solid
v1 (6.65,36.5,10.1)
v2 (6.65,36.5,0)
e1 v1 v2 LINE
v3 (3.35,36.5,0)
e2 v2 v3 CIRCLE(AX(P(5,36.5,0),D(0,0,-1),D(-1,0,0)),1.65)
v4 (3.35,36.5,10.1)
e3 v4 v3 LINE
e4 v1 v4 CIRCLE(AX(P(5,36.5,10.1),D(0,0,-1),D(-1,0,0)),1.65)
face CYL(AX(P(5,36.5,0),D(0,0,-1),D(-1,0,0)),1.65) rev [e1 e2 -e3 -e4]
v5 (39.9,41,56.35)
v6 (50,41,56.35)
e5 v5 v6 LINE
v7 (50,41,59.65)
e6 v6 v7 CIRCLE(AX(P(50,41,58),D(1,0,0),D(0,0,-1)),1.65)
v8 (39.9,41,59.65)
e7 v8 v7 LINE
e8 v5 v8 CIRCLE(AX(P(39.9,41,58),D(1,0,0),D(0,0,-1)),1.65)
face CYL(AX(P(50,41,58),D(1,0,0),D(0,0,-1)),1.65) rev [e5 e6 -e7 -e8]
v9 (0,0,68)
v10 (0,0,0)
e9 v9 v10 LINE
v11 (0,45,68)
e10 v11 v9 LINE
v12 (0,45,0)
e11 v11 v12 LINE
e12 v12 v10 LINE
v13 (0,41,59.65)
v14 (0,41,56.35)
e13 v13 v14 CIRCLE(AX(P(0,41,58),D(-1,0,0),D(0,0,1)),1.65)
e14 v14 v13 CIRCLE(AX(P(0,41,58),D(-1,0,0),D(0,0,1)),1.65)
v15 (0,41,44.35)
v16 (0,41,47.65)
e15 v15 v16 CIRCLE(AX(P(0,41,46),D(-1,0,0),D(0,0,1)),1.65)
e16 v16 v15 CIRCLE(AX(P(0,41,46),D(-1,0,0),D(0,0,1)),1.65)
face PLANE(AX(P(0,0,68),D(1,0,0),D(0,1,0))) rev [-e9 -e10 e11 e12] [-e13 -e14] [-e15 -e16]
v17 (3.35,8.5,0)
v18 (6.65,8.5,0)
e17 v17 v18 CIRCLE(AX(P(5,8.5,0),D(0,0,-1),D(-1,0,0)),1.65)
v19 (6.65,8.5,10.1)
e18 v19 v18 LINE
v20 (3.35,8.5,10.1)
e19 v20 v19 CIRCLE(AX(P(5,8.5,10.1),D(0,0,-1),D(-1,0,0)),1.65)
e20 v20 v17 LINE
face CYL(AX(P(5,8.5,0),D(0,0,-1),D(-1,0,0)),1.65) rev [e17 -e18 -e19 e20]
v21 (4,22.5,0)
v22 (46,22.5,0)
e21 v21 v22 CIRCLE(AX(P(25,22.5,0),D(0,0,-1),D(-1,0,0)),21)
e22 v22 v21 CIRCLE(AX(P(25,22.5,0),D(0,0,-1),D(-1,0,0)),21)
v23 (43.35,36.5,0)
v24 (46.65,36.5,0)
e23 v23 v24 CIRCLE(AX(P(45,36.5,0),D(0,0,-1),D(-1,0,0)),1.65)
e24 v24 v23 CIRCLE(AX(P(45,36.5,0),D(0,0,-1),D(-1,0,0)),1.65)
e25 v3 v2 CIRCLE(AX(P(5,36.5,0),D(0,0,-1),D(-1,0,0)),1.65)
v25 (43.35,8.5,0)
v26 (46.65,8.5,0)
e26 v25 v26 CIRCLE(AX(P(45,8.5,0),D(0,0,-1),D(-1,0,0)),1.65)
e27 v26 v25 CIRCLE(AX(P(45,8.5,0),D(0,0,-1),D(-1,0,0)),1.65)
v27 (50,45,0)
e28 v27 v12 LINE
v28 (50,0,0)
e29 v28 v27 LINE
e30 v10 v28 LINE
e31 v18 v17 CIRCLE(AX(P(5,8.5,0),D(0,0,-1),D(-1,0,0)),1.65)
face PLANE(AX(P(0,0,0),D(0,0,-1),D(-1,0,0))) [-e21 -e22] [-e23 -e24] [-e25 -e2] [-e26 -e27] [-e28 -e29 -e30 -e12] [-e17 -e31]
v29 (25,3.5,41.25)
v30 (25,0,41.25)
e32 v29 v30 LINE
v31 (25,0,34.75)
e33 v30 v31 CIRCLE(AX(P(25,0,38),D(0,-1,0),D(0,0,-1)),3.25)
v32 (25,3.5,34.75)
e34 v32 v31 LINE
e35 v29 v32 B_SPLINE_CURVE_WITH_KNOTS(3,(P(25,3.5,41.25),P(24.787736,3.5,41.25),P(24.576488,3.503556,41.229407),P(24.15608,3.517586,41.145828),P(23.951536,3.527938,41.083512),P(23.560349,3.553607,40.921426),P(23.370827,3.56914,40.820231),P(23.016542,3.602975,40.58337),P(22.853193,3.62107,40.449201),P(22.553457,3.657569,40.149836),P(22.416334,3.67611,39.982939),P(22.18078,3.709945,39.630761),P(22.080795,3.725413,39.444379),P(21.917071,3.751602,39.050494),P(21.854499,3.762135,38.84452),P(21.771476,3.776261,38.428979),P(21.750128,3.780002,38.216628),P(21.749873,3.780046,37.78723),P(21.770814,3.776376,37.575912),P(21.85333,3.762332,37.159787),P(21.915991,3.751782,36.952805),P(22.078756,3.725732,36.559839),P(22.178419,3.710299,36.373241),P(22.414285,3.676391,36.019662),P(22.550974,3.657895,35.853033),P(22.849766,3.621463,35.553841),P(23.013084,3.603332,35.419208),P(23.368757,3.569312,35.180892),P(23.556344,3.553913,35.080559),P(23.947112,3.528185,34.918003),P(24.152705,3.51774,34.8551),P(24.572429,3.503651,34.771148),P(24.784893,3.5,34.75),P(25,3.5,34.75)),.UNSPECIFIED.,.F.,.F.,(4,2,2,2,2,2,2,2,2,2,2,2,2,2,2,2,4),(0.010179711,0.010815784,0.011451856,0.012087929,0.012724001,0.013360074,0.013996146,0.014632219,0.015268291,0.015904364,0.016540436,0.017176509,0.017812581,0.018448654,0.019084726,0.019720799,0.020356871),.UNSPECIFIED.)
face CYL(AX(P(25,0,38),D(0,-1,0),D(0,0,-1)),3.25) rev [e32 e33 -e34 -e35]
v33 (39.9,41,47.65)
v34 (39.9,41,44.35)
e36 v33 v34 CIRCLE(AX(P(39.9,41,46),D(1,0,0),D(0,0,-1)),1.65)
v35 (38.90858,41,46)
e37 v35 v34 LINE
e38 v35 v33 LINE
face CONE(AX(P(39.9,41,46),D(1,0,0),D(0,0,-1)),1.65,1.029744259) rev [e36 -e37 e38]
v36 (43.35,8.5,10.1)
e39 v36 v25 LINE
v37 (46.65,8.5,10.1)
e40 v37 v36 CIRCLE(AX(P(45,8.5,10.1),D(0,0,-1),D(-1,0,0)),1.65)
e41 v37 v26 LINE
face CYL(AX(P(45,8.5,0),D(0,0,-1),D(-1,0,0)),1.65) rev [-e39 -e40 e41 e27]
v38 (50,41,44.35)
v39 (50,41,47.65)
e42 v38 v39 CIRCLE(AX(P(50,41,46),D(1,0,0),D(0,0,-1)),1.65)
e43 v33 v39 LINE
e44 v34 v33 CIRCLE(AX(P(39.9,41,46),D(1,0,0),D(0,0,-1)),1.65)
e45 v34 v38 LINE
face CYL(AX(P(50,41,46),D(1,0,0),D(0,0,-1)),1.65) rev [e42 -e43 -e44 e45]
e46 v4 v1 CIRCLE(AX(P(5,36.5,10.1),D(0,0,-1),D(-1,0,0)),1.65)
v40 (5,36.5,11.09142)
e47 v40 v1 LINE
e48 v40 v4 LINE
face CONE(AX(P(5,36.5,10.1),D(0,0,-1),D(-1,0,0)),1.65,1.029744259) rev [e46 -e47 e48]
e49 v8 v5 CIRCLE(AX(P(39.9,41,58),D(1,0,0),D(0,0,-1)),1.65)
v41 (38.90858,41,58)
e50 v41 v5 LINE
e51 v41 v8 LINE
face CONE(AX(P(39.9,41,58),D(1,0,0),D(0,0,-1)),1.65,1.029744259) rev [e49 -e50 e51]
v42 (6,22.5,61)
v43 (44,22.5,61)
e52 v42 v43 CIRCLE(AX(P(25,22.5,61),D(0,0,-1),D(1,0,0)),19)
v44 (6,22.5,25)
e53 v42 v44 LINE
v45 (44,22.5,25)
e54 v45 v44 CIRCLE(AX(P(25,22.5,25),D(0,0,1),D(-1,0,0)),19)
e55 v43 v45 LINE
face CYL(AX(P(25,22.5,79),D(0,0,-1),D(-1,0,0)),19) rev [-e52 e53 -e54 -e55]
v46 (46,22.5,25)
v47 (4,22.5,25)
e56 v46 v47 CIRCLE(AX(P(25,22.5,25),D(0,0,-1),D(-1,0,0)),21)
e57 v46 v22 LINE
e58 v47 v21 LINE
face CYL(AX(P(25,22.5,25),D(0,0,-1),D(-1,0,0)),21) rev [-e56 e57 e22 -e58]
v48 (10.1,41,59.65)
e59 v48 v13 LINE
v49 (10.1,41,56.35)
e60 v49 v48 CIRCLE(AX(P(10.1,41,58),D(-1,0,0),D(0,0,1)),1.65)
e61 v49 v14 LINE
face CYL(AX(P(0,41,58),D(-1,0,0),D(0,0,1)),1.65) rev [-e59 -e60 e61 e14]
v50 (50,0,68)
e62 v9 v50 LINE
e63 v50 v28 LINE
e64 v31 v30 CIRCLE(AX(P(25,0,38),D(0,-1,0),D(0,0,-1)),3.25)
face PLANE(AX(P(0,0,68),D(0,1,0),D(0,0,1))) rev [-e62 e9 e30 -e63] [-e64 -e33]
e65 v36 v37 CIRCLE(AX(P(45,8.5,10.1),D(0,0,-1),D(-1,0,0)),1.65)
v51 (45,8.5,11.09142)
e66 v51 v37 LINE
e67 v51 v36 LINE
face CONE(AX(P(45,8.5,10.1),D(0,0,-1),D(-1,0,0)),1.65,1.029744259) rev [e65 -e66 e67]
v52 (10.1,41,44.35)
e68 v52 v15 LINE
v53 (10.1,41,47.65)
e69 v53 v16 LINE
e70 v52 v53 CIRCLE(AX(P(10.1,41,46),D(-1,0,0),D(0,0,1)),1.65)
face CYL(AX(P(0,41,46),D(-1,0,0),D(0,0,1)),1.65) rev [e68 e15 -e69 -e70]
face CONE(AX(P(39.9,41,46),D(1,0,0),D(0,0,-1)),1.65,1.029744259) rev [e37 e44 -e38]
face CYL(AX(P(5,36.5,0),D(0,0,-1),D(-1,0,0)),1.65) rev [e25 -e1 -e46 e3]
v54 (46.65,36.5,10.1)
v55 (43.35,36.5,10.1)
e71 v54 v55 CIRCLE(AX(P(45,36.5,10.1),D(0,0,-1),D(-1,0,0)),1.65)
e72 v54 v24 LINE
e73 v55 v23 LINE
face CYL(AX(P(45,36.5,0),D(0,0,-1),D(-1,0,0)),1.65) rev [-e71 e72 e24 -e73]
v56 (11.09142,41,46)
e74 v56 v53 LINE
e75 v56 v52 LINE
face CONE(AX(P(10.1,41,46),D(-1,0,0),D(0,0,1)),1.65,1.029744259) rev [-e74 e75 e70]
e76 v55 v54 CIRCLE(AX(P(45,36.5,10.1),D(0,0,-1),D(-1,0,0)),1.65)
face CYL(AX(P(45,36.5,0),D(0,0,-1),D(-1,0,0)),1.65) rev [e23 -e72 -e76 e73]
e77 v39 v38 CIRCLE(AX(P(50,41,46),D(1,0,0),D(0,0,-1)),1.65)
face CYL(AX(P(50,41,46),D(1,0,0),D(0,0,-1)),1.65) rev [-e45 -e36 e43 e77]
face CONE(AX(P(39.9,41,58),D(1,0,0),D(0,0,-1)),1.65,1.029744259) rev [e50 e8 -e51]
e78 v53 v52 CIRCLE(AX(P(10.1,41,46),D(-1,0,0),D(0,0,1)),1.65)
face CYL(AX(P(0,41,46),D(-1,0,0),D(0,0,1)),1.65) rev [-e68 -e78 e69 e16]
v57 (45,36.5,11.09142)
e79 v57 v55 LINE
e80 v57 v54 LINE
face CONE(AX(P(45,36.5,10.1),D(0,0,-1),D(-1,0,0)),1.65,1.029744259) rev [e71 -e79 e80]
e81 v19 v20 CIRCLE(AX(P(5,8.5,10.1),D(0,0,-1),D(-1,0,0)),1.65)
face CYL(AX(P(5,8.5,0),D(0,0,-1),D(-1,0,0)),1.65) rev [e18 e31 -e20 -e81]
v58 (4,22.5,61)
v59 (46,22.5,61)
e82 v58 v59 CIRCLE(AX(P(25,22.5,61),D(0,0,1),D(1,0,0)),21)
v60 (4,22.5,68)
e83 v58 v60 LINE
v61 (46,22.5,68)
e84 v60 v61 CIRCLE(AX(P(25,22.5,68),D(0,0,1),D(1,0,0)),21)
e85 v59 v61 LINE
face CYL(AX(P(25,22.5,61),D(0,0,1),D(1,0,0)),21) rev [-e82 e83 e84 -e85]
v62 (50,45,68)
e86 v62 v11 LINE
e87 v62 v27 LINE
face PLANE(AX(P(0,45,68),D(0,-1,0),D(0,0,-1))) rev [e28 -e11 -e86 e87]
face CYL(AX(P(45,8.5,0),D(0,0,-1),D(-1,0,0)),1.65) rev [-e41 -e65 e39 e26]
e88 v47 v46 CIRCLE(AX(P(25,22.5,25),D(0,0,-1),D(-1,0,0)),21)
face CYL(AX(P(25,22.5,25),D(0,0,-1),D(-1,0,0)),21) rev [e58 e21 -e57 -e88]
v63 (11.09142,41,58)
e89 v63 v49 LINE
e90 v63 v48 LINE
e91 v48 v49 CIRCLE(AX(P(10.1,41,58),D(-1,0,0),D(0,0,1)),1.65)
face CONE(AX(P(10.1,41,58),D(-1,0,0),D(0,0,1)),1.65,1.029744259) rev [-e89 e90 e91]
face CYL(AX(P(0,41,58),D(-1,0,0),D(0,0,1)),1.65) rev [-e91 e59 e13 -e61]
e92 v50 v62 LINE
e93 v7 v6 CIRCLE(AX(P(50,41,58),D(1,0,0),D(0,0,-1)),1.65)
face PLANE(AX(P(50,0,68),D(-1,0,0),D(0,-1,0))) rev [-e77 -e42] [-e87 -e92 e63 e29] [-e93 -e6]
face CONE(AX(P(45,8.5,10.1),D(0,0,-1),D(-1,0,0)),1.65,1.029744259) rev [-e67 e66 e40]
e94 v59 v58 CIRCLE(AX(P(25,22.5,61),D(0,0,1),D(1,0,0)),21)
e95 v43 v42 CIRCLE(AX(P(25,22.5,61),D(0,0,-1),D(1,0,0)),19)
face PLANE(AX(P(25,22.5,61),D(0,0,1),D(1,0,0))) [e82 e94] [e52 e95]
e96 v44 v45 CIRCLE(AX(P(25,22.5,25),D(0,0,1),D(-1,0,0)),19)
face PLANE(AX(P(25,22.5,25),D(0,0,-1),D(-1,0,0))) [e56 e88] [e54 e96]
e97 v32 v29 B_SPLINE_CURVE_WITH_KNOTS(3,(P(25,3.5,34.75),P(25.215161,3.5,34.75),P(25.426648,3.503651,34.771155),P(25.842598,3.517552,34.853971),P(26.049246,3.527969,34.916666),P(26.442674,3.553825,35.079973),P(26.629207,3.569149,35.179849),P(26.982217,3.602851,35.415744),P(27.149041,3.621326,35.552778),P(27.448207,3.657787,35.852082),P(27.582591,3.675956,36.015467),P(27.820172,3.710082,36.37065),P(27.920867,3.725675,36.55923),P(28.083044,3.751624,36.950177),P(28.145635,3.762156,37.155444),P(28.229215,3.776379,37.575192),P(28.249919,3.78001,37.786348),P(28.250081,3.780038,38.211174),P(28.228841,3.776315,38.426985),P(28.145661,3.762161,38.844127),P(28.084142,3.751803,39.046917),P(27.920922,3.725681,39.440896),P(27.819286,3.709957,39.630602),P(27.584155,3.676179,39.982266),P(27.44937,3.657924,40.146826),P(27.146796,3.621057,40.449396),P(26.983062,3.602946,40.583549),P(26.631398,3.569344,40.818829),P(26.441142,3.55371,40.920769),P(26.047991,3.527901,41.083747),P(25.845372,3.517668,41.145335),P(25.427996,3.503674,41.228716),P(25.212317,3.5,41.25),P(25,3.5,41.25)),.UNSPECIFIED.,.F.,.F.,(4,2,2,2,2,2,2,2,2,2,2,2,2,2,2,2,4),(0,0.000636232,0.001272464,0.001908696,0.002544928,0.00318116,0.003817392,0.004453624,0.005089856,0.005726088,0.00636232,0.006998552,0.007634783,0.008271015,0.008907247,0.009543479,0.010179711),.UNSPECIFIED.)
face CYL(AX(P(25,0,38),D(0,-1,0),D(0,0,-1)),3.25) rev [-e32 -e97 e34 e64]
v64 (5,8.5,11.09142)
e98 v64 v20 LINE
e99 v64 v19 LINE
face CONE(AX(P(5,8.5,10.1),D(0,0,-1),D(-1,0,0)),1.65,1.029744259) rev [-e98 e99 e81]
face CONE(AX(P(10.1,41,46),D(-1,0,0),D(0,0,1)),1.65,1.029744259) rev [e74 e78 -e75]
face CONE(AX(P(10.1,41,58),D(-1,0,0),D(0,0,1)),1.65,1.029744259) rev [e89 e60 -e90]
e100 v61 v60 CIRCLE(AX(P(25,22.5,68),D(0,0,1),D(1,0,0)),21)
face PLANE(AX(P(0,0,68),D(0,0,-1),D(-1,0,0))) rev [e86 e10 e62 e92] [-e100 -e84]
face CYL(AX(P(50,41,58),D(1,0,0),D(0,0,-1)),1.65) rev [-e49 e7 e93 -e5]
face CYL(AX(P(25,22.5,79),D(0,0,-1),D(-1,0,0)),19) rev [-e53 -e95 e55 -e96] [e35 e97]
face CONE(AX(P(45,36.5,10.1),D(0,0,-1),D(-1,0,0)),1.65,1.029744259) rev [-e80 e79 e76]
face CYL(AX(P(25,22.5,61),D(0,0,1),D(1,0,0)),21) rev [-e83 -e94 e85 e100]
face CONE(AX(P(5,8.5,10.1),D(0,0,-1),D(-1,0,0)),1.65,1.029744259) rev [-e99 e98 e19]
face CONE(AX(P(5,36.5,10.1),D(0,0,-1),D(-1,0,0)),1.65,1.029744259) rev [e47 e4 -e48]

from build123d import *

# Parameters (mm, degrees)
SKETCH_1_W                  = 50
SKETCH_1_H                  = 45
EXTRUDE_1_DEPTH             = 68
SKETCH_2_R                  = 19
CUT_EXTRUDE_1_DEPTH         = 79
SKETCH_3_R                  = 21
CUT_EXTRUDE_2_DEPTH         = 7
CUT_EXTRUDE_START           = -25
SKETCH_4_R                  = 21
CUT_EXTRUDE_3_DEPTH         = 25
HOLE_WIZARD_M4_1_D          = 3.3
HOLE_WIZARD_M4_1_DEPTH      = 10.1
HOLE_WIZARD_M4_1_TIP        = 0.991420021
HOLE_WIZARD_M4_2_D          = 3.3
HOLE_WIZARD_M4_2_DEPTH      = 10.1
HOLE_WIZARD_M4_2_TIP        = 0.991420021
HOLE_WIZARD_6_5_6_5_1_D     = 6.5
HOLE_WIZARD_6_5_6_5_1_DEPTH = 20
HOLE_WIZARD_6_5_6_5_1_TIP   = 1.952797012
HOLE_WIZARD_M4_4_D          = 3.3
HOLE_WIZARD_M4_4_DEPTH      = 10.1
HOLE_WIZARD_M4_4_TIP        = 0.991420021


with BuildPart() as part:
    # 草图1 → 凸台-拉伸1 (new body)
    with BuildSketch(Plane.XY):
        with Locations((25, 22.5)):
            Rectangle(SKETCH_1_W, SKETCH_1_H)
    extrude(amount=EXTRUDE_1_DEPTH)

    # 草图2 → 切除-拉伸1 (cut)
    with BuildSketch(Plane(origin=(0, 0, 0), x_dir=(-1, 0, 0), z_dir=(0, 0, -1))):
        with Locations((-25, 22.5)):
            Circle(SKETCH_2_R)
    extrude(amount=-CUT_EXTRUDE_1_DEPTH, mode=Mode.SUBTRACT)

    # 草图3 → 切除-拉伸2 (cut)
    with BuildSketch(Plane.XY.offset(68)):
        with Locations((25, 22.5)):
            Circle(SKETCH_3_R)
    extrude(amount=-CUT_EXTRUDE_2_DEPTH, mode=Mode.SUBTRACT)

    # 草图4 → 切除-拉伸3 (cut)
    with BuildSketch(Plane(origin=(0, 0, 0), x_dir=(-1, 0, 0), z_dir=(0, 0, -1)).offset(CUT_EXTRUDE_START)):
        with Locations(Location((-25, 22.5, 0), (0, 0, 180))):
            Circle(SKETCH_4_R)
    extrude(amount=CUT_EXTRUDE_3_DEPTH, mode=Mode.SUBTRACT)

    # M4 螺纹孔1
    with Locations(Plane(origin=(50, 0, 0), x_dir=(0, 0, -1), z_dir=(1, 0, 0))):
        with Locations((-58, 41), (-46, 41)):
            Hole(HOLE_WIZARD_M4_1_D / 2, depth=HOLE_WIZARD_M4_1_DEPTH)
            with Locations((0, 0, -(HOLE_WIZARD_M4_1_DEPTH + HOLE_WIZARD_M4_1_TIP / 2))):  # 118° drill point
                Cone(0, HOLE_WIZARD_M4_1_D / 2, HOLE_WIZARD_M4_1_TIP, mode=Mode.SUBTRACT)

    # M4 螺纹孔2
    with Locations(Plane.ZY):
        with Locations((46, 41), (58, 41)):
            Hole(HOLE_WIZARD_M4_2_D / 2, depth=HOLE_WIZARD_M4_2_DEPTH)
            with Locations((0, 0, -(HOLE_WIZARD_M4_2_DEPTH + HOLE_WIZARD_M4_2_TIP / 2))):  # 118° drill point
                Cone(0, HOLE_WIZARD_M4_2_D / 2, HOLE_WIZARD_M4_2_TIP, mode=Mode.SUBTRACT)

    # Ø6.5 (6.5) 直径孔1
    with Locations(Plane(origin=(0, 0, 0), x_dir=(-1, 0, 0), z_dir=(0, -1, 0))):
        with Locations((-25, -38)):
            Hole(HOLE_WIZARD_6_5_6_5_1_D / 2, depth=HOLE_WIZARD_6_5_6_5_1_DEPTH)
            with Locations((0, 0, -(HOLE_WIZARD_6_5_6_5_1_DEPTH + HOLE_WIZARD_6_5_6_5_1_TIP / 2))):  # 118° drill point
                Cone(0, HOLE_WIZARD_6_5_6_5_1_D / 2, HOLE_WIZARD_6_5_6_5_1_TIP, mode=Mode.SUBTRACT)

    # M4 螺纹孔4
    with Locations(Plane(origin=(0, 0, 0), x_dir=(-1, 0, 0), z_dir=(0, 0, -1))):
        with Locations((-5, 36.5), (-45, 36.5), (-45, 8.5), (-5, 8.5)):
            Hole(HOLE_WIZARD_M4_4_D / 2, depth=HOLE_WIZARD_M4_4_DEPTH)
            with Locations((0, 0, -(HOLE_WIZARD_M4_4_DEPTH + HOLE_WIZARD_M4_4_TIP / 2))):  # 118° drill point
                Cone(0, HOLE_WIZARD_M4_4_D / 2, HOLE_WIZARD_M4_4_TIP, mode=Mode.SUBTRACT)


solid = part.part
